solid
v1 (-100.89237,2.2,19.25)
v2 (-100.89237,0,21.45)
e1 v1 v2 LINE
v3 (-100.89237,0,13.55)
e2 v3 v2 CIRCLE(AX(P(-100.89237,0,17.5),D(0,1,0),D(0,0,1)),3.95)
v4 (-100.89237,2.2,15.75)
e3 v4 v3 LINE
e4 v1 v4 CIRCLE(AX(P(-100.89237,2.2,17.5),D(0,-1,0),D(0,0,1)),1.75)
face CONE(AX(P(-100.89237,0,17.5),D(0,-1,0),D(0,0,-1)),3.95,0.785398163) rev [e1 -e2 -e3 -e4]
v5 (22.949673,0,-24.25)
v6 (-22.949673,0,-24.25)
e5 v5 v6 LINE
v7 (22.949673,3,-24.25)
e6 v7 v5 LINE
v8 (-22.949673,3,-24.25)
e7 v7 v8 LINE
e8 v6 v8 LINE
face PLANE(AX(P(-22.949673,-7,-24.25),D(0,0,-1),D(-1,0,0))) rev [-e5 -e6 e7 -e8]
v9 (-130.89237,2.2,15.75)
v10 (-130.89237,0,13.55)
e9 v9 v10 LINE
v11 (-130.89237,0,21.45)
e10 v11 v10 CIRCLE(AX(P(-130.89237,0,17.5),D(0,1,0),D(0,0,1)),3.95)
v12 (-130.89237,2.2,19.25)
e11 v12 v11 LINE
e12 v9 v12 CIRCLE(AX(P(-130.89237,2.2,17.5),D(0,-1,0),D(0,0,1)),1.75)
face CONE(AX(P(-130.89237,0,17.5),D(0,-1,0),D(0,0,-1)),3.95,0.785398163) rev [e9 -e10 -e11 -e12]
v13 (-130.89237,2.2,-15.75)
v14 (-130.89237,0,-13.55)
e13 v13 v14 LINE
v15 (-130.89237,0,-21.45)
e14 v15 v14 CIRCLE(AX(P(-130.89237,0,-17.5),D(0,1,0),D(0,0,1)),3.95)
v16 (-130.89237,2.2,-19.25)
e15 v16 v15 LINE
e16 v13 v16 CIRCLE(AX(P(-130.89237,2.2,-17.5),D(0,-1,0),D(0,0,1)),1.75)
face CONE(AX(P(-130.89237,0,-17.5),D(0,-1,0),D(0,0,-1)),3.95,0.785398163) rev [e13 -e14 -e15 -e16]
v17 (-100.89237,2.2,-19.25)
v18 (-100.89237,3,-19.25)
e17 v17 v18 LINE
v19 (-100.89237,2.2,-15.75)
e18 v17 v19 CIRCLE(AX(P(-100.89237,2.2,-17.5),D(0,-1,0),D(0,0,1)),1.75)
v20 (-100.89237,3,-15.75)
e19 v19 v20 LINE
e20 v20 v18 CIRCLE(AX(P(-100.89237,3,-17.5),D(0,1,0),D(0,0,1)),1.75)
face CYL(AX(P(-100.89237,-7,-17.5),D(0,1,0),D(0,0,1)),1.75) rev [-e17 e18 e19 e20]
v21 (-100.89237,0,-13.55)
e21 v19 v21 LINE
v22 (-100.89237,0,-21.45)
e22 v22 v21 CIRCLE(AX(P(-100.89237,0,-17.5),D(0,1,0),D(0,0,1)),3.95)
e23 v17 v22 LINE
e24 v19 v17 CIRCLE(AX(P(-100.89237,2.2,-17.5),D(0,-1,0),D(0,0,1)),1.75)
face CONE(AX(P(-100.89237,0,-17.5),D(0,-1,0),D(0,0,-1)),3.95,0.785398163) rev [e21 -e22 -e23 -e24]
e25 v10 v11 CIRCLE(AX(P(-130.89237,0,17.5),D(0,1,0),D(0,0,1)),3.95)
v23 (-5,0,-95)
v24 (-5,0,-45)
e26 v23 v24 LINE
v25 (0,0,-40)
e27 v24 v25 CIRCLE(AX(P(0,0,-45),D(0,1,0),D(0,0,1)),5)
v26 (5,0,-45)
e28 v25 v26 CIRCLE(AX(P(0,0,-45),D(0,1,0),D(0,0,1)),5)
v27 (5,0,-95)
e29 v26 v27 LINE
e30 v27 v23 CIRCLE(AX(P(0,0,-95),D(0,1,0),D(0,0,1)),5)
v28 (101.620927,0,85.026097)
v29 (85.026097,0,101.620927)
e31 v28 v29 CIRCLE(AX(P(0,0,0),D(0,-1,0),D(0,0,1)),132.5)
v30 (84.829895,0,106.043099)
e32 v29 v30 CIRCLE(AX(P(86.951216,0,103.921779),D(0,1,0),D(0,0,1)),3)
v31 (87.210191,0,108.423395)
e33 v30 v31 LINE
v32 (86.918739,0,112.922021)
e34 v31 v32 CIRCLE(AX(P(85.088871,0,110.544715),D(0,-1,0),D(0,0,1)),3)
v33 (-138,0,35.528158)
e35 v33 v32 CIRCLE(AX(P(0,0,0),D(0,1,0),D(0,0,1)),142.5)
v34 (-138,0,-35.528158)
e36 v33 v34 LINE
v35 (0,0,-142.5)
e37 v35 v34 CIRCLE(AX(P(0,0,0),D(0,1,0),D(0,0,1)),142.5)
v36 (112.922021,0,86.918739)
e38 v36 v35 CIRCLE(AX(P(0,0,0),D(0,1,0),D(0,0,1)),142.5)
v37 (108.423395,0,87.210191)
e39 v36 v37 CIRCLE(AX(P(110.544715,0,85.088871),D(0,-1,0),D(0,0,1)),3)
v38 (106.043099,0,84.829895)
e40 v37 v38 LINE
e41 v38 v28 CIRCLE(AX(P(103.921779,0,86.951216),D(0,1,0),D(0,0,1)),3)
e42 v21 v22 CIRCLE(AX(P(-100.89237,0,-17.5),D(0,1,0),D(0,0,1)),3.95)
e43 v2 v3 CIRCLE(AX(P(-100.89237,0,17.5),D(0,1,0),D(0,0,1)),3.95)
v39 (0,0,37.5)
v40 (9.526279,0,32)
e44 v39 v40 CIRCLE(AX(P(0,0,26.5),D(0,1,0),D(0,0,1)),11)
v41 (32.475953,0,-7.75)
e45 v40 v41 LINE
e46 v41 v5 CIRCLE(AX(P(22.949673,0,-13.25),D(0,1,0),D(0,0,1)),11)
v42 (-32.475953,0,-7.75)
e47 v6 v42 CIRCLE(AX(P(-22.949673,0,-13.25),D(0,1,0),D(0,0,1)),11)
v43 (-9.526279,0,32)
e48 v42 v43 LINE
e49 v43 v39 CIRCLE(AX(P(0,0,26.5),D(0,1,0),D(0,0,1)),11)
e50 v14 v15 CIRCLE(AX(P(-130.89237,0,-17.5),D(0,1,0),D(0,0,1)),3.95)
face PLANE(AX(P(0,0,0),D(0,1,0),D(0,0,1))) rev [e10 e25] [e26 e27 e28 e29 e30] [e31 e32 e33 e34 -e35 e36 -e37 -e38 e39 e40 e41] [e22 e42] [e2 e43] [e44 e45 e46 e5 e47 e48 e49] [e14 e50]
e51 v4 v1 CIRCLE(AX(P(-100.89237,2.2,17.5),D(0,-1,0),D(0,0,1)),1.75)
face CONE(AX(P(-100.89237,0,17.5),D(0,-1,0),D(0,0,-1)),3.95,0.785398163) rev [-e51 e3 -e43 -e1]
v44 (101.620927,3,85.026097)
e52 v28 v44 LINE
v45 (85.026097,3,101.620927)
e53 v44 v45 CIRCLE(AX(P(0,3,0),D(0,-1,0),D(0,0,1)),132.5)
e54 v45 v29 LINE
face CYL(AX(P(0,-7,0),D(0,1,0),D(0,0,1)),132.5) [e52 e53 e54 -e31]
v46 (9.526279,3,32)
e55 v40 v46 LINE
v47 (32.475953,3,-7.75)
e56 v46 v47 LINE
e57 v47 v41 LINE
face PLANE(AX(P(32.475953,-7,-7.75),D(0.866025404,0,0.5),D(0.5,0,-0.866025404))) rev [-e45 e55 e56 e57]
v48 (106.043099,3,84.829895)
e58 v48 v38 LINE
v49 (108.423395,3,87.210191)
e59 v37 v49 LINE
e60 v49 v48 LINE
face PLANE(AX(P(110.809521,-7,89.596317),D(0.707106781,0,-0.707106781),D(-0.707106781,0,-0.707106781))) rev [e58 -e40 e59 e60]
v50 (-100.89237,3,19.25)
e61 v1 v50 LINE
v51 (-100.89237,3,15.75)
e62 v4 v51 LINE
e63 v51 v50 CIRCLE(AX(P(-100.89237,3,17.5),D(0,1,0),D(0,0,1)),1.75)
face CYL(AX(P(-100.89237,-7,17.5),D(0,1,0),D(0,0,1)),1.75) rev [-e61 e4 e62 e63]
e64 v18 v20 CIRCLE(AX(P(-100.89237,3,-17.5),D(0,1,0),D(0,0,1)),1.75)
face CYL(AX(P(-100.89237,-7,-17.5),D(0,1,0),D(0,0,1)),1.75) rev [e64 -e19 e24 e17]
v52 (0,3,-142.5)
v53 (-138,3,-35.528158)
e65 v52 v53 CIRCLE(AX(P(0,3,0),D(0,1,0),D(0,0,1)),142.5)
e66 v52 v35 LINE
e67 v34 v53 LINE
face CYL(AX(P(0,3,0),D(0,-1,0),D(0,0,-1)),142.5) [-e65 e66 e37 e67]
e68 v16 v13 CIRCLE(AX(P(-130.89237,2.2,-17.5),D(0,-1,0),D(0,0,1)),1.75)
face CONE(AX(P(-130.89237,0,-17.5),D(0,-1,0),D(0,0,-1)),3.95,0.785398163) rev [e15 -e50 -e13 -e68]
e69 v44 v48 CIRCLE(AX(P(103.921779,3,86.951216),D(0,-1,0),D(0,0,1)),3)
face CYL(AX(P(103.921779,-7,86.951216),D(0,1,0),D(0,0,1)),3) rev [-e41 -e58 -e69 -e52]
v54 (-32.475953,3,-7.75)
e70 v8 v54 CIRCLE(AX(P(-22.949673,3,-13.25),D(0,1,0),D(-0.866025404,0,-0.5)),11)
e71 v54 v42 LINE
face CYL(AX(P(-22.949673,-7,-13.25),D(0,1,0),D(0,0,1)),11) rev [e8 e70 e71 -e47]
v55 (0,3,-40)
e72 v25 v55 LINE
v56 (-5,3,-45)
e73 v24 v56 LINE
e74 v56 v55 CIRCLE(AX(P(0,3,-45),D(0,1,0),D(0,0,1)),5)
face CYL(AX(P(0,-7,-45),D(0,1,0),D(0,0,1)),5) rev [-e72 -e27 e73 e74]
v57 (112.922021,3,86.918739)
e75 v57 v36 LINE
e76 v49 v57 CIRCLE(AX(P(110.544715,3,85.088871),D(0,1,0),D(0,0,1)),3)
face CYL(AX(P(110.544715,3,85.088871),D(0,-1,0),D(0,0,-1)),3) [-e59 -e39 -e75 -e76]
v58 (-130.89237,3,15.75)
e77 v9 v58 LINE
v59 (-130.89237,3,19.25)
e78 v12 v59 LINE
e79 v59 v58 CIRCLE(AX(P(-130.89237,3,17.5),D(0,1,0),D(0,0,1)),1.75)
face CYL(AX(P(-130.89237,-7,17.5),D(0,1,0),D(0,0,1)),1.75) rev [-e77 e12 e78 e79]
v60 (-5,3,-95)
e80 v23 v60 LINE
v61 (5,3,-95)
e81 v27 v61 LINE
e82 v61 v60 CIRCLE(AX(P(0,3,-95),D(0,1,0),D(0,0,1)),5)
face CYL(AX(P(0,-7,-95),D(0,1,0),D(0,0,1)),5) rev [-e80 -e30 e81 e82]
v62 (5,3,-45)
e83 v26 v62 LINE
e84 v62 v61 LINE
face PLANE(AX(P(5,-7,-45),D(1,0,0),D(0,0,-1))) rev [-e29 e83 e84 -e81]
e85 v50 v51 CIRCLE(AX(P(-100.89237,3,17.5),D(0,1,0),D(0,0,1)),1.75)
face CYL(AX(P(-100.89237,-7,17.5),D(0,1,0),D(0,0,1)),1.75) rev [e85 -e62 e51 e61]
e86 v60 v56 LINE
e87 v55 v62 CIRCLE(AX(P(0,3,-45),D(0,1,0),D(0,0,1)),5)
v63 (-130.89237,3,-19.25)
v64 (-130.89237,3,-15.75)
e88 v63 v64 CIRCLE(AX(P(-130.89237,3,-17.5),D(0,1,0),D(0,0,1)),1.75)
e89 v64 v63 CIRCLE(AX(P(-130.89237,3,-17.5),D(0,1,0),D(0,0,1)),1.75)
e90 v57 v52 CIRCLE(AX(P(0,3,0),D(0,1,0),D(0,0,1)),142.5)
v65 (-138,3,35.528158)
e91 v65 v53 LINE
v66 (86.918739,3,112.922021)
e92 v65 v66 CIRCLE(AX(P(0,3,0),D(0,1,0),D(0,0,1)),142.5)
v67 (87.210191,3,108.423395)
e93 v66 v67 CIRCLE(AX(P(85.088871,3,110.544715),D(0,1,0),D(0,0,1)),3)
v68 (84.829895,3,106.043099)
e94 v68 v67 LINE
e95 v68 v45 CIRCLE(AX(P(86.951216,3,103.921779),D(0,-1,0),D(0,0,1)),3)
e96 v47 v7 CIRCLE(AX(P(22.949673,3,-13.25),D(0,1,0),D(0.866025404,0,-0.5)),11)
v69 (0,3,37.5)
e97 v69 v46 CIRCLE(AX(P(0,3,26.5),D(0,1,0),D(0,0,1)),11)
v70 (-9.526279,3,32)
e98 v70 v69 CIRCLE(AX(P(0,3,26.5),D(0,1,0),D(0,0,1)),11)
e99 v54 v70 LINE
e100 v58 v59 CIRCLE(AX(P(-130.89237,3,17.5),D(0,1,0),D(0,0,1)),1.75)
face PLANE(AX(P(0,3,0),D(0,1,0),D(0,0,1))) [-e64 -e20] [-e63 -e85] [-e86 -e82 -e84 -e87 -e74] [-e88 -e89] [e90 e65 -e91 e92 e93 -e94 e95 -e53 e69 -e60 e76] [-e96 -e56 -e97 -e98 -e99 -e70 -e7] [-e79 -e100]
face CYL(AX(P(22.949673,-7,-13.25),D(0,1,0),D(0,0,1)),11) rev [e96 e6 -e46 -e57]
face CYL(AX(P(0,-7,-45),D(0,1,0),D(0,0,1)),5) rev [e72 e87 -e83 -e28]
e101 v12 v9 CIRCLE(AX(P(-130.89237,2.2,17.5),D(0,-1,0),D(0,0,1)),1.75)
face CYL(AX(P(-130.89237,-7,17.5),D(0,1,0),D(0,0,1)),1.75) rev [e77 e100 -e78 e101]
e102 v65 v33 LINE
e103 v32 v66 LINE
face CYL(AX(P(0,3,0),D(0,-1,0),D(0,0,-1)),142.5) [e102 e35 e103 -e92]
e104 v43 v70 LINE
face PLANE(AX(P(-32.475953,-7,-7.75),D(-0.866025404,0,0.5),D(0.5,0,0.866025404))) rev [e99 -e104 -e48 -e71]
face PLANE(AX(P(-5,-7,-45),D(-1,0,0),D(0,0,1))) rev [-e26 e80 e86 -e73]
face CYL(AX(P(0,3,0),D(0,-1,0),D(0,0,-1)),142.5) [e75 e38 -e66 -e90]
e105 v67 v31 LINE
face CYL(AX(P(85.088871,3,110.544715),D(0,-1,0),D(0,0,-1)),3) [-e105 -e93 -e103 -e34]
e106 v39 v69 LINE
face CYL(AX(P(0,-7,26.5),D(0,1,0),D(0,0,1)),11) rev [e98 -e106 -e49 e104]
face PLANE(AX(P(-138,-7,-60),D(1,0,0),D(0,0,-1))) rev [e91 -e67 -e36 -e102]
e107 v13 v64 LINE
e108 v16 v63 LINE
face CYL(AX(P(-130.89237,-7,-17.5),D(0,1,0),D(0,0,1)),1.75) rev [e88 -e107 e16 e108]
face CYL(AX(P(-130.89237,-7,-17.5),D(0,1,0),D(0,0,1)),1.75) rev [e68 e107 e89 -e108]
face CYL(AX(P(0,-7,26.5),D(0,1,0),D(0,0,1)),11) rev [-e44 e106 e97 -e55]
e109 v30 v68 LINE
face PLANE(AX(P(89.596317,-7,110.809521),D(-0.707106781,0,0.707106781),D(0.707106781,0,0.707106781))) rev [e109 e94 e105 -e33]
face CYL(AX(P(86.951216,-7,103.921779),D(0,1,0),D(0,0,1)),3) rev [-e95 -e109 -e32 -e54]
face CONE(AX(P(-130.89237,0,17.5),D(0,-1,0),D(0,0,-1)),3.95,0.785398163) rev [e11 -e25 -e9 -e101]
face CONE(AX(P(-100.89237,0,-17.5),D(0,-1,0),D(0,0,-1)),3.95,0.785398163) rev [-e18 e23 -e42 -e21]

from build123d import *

# Parameters (mm, degrees)
SKETCH1_R           = 142.5
BOSS_EXTRUDE1_DEPTH = 3
SKETCH3_R           = 11
CUT_EXTRUDE1_DEPTH  = 10
CIRPATTERN1_COUNT   = 3
CUT_EXTRUDE2_DEPTH  = 10
CUT_EXTRUDE3_DEPTH  = 10
CUT_EXTRUDE6_START  = -10
CUT_EXTRUDE6_DEPTH  = 10
FILLET1_R           = 3
SKETCH7_W           = 9
SKETCH7_H           = 120
CUT_EXTRUDE7_DEPTH  = 10
SKETCH8_R           = 1.75
CUT_EXTRUDE8_DEPTH  = 10
CHAMFER1_SIZE       = 2.2


with BuildPart() as part:
    # Sketch1 → Boss-Extrude1 (new body)
    with BuildSketch(Plane(origin=(0, 0, 0), x_dir=(1, 0, 0), z_dir=(0, 1, 0))):
        with Locations(Location((0, 0, 0), (0, 0, 270))):
            Circle(SKETCH1_R)
    extrude(amount=BOSS_EXTRUDE1_DEPTH)

    # Sketch3 → Cut-Extrude1 (cut)
    with BuildSketch(Plane(origin=(0, 3, 0), x_dir=(1, 0, 0), z_dir=(0, 1, 0))):
        with Locations(Location((0, -26.5, 0), (0, 0, 270))):
            Circle(SKETCH3_R)
    cut_extrude1 = extrude(amount=-CUT_EXTRUDE1_DEPTH, mode=Mode.SUBTRACT)

    # CirPattern1: Cut-Extrude1 ×3 about axis
    cirpattern1_axis = Axis((0, 0, 0), (0, 1, 0))
    for i in range(1, CIRPATTERN1_COUNT):
        add(cut_extrude1.rotate(cirpattern1_axis, i * 360 / CIRPATTERN1_COUNT), mode=Mode.SUBTRACT)

    # Sketch4 → Cut-Extrude2 (cut)
    with BuildSketch(Plane(origin=(0, 3, 0), x_dir=(1, 0, 0), z_dir=(0, 1, 0))):
        with BuildLine():
            Line((-32.475952642, 7.75), (-9.526279442, -32))
            ThreePointArc((-9.526279442, -32), (0, -37.5), (9.526279442, -32))
            Line((9.526279442, -32), (32.475952642, 7.75))
            ThreePointArc((32.475952642, 7.75), (32.475952642, 18.75), (22.9496732, 24.25))
            Line((22.9496732, 24.25), (-22.9496732, 24.25))
            ThreePointArc((-22.9496732, 24.25), (-32.475952642, 18.75), (-32.475952642, 7.75))
        make_face()
    extrude(amount=-CUT_EXTRUDE2_DEPTH, mode=Mode.SUBTRACT)

    # Sketch5 → Cut-Extrude3 (cut)
    with BuildSketch(Plane(origin=(0, 3, 0), x_dir=(1, 0, 0), z_dir=(0, 1, 0))):
        with BuildLine():
            Line((-5, 45), (-5, 95))
            ThreePointArc((-5, 95), (0, 100), (5, 95))
            Line((5, 95), (5, 45))
            ThreePointArc((5, 45), (0, 40), (-5, 45))
        make_face()
    extrude(amount=-CUT_EXTRUDE3_DEPTH, mode=Mode.SUBTRACT)

    # Sketch6 → Cut-Extrude6 (cut)
    with BuildSketch(Plane(origin=(0, 3, 0), x_dir=(1, 0, 0), z_dir=(0, 1, 0)).offset(CUT_EXTRUDE6_START)):
        with BuildLine():
            Line((89.596317401, -110.809520837), (82.482737092, -103.695940527))
            ThreePointArc((82.482737092, -103.695940527), (93.691648507, -93.691648507), (103.695940527, -82.482737092))
            Line((103.695940527, -82.482737092), (110.809520837, -89.596317401))
            ThreePointArc((110.809520837, -89.596317401), (100.762716319, -100.762716319), (89.596317401, -110.809520837))
        make_face()
    extrude(amount=CUT_EXTRUDE6_DEPTH, mode=Mode.SUBTRACT)

    # Fillet1
    fillet1_edges = [part.edges().sort_by_distance(p)[0] for p in [
        (82.482737092, 1.5, 103.695940527),
        (103.695940527, 1.5, 82.482737092),
        (110.809520837, 1.5, 89.596317401),
        (89.596317401, 1.5, 110.809520837),
    ]]
    fillet(fillet1_edges, radius=FILLET1_R)

    # Sketch7 → Cut-Extrude7 (cut)
    with BuildSketch(Plane(origin=(0, 3, 0), x_dir=(1, 0, 0), z_dir=(0, 1, 0))):
        with Locations((-142.5, 0)):
            Rectangle(SKETCH7_W, SKETCH7_H)
    extrude(amount=-CUT_EXTRUDE7_DEPTH, mode=Mode.SUBTRACT)

    # Sketch8 → Cut-Extrude8 (cut)
    with BuildSketch(Plane(origin=(0, 3, 0), x_dir=(1, 0, 0), z_dir=(0, 1, 0))):
        with Locations(Location((-130.892369907, 17.5, 0), (0, 0, 270))):
            Circle(SKETCH8_R)
        with Locations(Location((-100.892369907, 17.5, 0), (0, 0, 270))):
            Circle(SKETCH8_R)
        with Locations(Location((-130.892369907, -17.5, 0), (0, 0, 270))):
            Circle(SKETCH8_R)
        with Locations(Location((-100.892369907, -17.5, 0), (0, 0, 270))):
            Circle(SKETCH8_R)
    extrude(amount=-CUT_EXTRUDE8_DEPTH, mode=Mode.SUBTRACT)

    # Chamfer1
    chamfer1_edges = [part.edges().sort_by_distance(p)[0] for p in [
        (-130.892369907, 0, -19.25),
        (-100.892369907, 0, -19.25),
        (-130.892369907, 0, 15.75),
        (-100.892369907, 0, 15.75),
    ]]
    chamfer(chamfer1_edges, length=CHAMFER1_SIZE)


solid = part.part
